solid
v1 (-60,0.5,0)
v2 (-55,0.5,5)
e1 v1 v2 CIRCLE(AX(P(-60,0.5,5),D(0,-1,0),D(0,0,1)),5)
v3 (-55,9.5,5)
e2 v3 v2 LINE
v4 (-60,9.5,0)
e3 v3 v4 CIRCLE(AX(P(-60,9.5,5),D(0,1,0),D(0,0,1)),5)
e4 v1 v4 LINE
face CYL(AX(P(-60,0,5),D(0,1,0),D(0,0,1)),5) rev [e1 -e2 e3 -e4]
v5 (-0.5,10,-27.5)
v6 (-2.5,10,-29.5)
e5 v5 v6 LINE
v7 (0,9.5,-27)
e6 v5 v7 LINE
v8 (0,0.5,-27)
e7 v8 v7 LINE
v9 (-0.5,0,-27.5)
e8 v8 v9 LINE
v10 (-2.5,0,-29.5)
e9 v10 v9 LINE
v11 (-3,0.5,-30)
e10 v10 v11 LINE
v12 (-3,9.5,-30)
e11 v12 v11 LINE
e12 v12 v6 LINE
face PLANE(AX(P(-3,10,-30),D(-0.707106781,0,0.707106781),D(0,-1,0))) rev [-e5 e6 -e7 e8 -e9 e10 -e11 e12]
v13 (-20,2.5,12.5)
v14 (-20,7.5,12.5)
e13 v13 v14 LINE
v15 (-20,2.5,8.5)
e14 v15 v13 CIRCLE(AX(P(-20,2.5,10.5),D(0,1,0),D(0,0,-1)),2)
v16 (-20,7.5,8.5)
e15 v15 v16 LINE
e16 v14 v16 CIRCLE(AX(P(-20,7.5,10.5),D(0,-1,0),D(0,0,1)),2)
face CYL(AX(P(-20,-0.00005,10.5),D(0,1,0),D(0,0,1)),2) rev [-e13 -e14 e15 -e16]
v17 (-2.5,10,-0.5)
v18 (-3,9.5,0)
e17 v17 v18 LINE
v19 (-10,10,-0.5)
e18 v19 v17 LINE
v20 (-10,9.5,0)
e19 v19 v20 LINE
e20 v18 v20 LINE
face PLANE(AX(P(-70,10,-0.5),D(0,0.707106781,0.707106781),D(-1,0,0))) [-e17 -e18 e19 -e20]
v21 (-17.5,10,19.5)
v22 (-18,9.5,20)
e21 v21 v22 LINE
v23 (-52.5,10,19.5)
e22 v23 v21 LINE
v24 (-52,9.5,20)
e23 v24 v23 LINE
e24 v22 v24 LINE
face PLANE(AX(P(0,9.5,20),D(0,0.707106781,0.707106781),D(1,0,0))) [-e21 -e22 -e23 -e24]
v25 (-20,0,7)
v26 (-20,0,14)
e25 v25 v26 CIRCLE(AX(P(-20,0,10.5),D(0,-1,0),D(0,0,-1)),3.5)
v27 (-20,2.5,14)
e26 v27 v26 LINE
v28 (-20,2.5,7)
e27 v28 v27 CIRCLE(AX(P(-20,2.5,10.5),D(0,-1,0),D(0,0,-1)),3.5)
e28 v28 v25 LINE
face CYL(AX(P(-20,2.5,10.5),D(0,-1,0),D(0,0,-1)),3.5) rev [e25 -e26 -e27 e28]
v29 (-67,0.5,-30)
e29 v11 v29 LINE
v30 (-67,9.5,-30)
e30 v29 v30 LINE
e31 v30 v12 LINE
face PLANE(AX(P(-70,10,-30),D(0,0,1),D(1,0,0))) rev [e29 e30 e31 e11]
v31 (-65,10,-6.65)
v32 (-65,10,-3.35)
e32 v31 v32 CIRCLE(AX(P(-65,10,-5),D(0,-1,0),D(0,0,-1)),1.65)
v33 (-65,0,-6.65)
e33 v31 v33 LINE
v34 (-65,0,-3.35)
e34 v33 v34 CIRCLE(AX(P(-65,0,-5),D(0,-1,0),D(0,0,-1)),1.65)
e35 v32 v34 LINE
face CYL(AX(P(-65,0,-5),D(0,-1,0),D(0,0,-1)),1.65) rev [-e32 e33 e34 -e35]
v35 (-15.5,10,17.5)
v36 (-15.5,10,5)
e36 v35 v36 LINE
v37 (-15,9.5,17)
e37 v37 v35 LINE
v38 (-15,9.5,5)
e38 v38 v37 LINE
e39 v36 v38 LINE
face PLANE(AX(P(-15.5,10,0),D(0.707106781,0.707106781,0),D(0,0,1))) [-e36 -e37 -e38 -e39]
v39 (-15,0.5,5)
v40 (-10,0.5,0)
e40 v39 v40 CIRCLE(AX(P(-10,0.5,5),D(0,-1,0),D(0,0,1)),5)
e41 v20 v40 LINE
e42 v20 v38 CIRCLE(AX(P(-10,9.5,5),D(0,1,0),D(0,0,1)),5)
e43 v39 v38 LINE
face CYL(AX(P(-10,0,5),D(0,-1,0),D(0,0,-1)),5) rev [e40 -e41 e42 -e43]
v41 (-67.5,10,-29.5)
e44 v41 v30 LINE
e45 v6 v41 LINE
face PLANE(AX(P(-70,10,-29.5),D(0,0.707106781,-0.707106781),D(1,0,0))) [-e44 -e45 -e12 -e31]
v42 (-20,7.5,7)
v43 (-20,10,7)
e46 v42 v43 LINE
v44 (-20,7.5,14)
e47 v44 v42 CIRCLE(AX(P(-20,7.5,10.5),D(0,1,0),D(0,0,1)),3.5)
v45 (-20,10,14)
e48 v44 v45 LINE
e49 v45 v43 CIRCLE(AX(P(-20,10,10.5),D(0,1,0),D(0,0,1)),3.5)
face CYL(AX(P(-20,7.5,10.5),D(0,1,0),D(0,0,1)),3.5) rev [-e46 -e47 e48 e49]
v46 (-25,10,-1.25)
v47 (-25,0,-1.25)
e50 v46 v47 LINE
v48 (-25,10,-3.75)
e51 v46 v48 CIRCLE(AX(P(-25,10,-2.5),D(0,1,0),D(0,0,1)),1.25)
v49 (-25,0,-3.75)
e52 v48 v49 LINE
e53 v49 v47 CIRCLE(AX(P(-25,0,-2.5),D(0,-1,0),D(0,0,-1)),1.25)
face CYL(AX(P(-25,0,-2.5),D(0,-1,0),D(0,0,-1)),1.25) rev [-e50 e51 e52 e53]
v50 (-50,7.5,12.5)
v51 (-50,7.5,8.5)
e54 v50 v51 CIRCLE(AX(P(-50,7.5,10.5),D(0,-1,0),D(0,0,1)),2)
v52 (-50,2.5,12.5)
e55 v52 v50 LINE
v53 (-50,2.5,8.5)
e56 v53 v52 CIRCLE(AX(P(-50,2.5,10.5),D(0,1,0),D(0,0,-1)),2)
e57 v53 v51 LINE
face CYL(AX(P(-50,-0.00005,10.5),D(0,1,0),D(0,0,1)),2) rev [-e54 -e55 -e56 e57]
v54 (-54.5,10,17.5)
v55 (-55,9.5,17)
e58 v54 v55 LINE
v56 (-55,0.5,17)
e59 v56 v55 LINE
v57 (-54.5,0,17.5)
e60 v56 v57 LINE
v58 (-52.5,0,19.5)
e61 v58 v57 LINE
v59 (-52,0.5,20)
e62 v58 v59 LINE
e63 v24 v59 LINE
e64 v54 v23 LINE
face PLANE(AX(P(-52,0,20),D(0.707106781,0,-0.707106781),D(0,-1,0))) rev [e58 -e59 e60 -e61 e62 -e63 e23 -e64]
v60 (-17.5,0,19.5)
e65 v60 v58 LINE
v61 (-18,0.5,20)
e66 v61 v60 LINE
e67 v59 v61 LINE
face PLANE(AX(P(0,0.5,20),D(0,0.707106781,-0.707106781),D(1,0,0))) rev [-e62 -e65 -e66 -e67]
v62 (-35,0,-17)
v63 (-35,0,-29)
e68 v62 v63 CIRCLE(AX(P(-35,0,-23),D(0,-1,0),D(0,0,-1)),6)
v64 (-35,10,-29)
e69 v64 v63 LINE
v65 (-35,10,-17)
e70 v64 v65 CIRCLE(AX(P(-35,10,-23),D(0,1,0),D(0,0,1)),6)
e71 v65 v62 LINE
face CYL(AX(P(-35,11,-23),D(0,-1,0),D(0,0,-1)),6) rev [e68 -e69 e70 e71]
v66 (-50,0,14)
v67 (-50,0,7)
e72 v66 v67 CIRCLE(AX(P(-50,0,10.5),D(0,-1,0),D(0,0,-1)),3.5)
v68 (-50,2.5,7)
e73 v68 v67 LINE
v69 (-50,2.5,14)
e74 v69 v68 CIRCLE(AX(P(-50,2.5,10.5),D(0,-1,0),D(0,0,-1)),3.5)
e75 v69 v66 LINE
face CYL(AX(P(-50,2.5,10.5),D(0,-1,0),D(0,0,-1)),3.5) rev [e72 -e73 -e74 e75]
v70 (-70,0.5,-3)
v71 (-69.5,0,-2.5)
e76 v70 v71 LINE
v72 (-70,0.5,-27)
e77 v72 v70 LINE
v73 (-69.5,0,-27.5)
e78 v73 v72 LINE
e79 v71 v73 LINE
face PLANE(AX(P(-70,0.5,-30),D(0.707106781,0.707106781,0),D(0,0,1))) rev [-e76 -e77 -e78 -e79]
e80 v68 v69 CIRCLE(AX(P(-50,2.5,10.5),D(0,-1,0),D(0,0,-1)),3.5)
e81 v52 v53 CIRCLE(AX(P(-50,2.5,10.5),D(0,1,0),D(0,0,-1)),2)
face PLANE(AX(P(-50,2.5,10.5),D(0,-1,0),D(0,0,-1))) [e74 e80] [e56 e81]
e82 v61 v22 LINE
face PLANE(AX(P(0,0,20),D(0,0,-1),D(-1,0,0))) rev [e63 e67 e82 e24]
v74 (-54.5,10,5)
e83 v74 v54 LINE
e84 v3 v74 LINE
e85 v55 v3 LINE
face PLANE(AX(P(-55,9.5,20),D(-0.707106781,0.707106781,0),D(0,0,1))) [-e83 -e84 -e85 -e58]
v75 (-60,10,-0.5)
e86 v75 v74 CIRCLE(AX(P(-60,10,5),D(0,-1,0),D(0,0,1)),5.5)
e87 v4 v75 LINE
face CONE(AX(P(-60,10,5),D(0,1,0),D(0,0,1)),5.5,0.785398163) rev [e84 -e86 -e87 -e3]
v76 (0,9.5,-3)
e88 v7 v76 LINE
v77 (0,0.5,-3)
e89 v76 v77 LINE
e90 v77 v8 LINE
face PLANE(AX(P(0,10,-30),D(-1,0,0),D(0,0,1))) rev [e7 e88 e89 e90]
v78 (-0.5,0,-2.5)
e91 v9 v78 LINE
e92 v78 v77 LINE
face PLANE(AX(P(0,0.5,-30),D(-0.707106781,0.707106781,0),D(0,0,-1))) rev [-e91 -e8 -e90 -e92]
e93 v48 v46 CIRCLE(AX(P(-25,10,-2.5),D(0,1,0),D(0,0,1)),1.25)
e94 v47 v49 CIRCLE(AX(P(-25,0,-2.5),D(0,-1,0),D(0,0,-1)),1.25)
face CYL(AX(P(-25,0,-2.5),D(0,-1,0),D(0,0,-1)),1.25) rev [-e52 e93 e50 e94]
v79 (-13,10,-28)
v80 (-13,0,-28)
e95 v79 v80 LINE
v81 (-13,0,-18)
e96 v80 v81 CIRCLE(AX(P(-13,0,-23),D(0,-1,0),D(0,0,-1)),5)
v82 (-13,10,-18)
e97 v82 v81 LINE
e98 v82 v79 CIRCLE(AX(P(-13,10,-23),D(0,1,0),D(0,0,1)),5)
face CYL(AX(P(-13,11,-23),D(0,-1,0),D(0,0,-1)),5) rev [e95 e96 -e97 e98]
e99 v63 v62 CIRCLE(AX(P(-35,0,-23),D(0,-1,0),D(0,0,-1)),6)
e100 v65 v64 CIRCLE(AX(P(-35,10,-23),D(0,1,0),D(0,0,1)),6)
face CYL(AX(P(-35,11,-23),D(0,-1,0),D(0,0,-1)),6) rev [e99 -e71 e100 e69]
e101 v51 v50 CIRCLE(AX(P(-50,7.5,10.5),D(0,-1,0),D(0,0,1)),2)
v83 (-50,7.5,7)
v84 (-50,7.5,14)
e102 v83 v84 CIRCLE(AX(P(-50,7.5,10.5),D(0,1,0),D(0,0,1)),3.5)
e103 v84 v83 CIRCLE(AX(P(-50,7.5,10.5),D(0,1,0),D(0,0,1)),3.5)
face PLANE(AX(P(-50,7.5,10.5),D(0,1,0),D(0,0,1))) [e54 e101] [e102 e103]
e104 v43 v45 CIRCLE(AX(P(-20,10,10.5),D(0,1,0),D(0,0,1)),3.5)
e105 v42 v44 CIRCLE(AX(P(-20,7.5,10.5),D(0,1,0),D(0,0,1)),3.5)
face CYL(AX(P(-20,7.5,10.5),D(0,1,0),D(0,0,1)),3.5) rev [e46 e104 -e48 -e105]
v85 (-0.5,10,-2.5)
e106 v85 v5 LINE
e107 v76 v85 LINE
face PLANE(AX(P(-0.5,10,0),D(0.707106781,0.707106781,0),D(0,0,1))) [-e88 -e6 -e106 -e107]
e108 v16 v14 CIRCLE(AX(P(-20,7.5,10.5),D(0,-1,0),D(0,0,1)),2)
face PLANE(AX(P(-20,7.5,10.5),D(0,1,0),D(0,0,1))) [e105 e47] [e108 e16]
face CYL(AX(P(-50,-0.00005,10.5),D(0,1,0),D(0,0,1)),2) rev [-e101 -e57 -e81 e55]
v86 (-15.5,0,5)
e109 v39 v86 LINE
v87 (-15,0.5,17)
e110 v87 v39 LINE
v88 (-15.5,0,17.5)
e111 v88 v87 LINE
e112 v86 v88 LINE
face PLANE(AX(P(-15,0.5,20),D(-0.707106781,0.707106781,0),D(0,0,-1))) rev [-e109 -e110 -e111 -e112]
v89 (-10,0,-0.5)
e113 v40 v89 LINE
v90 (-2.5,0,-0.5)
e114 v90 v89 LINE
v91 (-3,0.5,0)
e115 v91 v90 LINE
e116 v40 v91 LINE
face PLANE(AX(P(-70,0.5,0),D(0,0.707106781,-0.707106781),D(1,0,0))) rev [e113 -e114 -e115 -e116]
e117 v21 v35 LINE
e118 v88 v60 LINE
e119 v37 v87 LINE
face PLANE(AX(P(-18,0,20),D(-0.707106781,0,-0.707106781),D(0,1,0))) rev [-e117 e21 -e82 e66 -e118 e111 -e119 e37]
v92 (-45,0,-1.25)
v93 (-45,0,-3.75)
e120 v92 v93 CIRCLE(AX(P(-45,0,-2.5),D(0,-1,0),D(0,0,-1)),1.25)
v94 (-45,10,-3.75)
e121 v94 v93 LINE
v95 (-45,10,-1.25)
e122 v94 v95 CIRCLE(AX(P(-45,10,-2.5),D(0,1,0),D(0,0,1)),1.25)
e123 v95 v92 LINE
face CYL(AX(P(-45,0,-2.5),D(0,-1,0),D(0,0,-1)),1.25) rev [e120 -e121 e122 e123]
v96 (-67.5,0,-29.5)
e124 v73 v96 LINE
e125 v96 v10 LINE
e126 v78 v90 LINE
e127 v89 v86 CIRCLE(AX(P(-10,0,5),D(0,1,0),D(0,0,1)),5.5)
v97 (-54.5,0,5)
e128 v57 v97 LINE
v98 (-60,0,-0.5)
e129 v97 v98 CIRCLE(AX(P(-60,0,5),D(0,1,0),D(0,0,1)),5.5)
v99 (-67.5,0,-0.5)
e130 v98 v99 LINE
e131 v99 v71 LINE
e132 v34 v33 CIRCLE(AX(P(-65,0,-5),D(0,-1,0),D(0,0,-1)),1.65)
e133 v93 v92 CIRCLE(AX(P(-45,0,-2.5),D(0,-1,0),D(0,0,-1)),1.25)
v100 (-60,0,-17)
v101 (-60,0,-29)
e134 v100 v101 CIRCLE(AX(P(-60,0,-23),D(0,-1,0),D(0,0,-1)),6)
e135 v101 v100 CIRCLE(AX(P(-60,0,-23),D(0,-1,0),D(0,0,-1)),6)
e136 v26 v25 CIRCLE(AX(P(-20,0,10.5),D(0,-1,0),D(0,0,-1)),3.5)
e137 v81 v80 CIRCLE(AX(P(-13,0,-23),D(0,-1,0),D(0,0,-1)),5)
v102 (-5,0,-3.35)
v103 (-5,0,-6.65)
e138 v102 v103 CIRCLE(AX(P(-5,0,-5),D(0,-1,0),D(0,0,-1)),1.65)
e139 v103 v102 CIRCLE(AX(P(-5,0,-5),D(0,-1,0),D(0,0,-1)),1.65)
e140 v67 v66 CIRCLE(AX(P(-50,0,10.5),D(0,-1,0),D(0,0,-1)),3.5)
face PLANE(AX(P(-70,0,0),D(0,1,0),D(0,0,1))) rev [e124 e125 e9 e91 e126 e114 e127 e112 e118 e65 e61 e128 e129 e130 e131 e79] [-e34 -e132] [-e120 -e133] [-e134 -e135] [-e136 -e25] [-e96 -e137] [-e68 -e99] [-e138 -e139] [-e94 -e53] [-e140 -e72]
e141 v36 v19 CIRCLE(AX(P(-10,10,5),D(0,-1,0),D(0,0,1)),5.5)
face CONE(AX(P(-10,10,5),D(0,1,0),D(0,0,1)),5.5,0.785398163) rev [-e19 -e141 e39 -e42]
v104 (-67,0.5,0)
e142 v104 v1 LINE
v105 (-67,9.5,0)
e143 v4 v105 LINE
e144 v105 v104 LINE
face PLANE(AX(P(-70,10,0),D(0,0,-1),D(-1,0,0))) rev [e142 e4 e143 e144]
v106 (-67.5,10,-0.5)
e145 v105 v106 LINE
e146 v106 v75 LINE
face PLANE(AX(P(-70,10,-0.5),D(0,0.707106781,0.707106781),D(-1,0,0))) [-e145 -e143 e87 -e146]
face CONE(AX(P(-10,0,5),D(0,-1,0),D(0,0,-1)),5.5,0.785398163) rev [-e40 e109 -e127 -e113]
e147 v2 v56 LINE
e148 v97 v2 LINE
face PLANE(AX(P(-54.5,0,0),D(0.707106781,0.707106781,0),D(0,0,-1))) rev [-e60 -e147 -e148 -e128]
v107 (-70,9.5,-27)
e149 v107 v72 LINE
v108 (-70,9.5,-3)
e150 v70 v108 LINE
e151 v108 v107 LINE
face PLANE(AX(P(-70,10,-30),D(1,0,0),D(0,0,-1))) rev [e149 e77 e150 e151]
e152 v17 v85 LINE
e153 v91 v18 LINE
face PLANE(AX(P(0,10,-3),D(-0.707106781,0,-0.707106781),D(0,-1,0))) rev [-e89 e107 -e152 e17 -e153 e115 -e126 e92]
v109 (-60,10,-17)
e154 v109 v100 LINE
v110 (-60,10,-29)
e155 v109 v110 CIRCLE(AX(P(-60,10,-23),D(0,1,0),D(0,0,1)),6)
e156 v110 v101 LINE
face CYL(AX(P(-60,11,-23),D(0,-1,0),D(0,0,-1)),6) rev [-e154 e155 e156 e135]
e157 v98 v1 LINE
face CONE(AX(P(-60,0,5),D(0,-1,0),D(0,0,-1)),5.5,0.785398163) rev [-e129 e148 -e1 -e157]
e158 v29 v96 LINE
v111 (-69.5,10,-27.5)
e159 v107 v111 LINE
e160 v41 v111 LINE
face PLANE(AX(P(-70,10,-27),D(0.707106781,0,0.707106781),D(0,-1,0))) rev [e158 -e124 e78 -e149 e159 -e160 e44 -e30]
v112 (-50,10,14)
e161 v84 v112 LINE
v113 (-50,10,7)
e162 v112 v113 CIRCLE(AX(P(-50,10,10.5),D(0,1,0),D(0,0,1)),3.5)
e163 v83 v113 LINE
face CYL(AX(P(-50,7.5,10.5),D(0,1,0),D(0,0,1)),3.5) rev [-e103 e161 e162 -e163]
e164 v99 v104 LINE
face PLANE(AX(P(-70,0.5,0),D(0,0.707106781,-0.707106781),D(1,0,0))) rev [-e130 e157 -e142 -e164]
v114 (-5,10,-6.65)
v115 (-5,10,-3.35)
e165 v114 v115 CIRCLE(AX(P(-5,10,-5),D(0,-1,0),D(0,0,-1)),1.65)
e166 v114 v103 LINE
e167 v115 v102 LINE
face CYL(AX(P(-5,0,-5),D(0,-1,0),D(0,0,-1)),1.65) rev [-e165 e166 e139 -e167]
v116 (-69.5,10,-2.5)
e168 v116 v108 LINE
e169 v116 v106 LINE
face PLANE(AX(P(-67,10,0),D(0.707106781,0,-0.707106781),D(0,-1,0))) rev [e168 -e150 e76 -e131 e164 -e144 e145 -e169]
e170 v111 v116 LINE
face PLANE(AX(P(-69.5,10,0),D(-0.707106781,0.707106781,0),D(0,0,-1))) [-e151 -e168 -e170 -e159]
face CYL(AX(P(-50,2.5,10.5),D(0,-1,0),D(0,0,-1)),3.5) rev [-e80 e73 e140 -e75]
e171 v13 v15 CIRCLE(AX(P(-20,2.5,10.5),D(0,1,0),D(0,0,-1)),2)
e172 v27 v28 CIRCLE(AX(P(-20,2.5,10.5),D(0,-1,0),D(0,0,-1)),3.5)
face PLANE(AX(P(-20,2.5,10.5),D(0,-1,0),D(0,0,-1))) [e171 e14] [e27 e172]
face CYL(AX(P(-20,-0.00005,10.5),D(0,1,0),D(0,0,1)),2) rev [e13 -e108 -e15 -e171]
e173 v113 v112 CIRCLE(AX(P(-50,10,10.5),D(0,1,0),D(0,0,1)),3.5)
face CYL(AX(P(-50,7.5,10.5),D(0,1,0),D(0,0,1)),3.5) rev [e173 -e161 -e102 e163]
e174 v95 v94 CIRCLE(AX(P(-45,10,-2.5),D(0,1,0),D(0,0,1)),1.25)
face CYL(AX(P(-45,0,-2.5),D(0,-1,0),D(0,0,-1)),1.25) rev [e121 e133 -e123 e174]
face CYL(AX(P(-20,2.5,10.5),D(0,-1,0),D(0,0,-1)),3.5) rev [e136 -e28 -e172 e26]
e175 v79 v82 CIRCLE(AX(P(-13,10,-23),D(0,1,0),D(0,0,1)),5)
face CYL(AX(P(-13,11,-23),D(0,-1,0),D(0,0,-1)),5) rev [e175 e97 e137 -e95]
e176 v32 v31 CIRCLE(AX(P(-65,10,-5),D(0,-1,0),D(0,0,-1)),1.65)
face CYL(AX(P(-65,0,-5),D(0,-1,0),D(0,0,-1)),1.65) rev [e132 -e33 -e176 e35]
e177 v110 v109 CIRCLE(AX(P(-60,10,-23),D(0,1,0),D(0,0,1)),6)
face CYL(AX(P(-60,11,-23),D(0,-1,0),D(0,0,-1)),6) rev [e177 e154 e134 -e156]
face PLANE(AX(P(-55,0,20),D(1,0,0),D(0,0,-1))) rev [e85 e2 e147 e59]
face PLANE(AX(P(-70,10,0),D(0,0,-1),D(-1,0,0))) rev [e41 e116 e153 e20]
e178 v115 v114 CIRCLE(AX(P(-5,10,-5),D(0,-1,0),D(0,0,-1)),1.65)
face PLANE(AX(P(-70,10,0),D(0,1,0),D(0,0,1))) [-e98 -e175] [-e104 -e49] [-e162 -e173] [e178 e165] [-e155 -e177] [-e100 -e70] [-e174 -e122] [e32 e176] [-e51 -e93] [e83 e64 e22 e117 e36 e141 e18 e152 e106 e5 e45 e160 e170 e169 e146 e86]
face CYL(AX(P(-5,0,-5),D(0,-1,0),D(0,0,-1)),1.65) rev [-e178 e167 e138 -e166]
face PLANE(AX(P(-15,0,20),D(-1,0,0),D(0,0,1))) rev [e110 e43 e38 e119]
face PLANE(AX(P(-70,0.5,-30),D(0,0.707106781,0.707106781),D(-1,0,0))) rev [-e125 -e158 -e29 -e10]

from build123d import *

# Parameters (mm, degrees)
SKETCH1_W           = 70
SKETCH1_H           = 30
BOSS_EXTRUDE1_DEPTH = 10
SKETCH8_R           = 5
CUT_EXTRUDE6_DEPTH  = 11
SKETCH9_R           = 6
CUT_EXTRUDE7_DEPTH  = 11
M4_TAPPED_HOLE2_D   = 3.3
SKETCH13_W          = 40
SKETCH13_H          = 10
BOSS_EXTRUDE2_DEPTH = 20
SKETCH14_R          = 2
CUT_EXTRUDE8_DEPTH  = 77.811457479
M3_TAPPED_HOLE1_D   = 2.5
CHAMFER3_SIZE       = 3
FILLET1_R           = 5
CHAMFER4_SIZE       = 0.5
SKETCH18_R          = 3.5
CUT_EXTRUDE9_DEPTH  = 2.5
CUT_EXTRUDE10_START = -2.5
SKETCH19_R          = 3.5
CUT_EXTRUDE10_DEPTH = 2.5


with BuildPart() as part:
    # Sketch1 → Boss-Extrude1 (new body)
    with BuildSketch(Plane(origin=(0, 0, 0), x_dir=(1, 0, 0), z_dir=(0, 1, 0))):
        with Locations((-35, 15)):
            Rectangle(SKETCH1_W, SKETCH1_H)
    extrude(amount=BOSS_EXTRUDE1_DEPTH)

    # Sketch8 → Cut-Extrude6 (cut)
    with BuildSketch(Plane.XZ):
        with Locations(Location((-13, -23, 0), (0, 0, 270))):
            Circle(SKETCH8_R)
    extrude(amount=-CUT_EXTRUDE6_DEPTH, mode=Mode.SUBTRACT)

    # Sketch9 → Cut-Extrude7 (cut)
    with BuildSketch(Plane.XZ):
        with Locations(Location((-60, -23, 0), (0, 0, 270))):
            Circle(SKETCH9_R)
        with Locations(Location((-35, -23, 0), (0, 0, 270))):
            Circle(SKETCH9_R)
    extrude(amount=-CUT_EXTRUDE7_DEPTH, mode=Mode.SUBTRACT)

    # M4 Tapped Hole2 (through all)
    with Locations(Plane(origin=(0, 0, 0), x_dir=(-1, 0, 0), z_dir=(0, -1, 0))):
        with Locations((65, 5), (5, 5)):
            Hole(M4_TAPPED_HOLE2_D / 2)

    # Sketch13 → Boss-Extrude2 (add)
    with BuildSketch(Plane.XY):
        with Locations((-35, 5)):
            Rectangle(SKETCH13_W, SKETCH13_H)
    extrude(amount=BOSS_EXTRUDE2_DEPTH)

    # Sketch14 → Cut-Extrude8 (cut, through all)
    with BuildSketch(Plane(origin=(0, 10, 0), x_dir=(1, 0, 0), z_dir=(0, 1, 0))):
        with Locations(Location((-50, -10.5, 0), (0, 0, 270))):
            Circle(SKETCH14_R)
        with Locations(Location((-20, -10.5, 0), (0, 0, 270))):
            Circle(SKETCH14_R)
    extrude(amount=-CUT_EXTRUDE8_DEPTH, mode=Mode.SUBTRACT)

    # M3 Tapped Hole1 (through all)
    with Locations(Plane(origin=(0, 0, 0), x_dir=(-1, 0, 0), z_dir=(0, -1, 0))):
        with Locations((25, 2.5), (45, 2.5)):
            Hole(M3_TAPPED_HOLE1_D / 2)

    # Chamfer3
    chamfer3_edges = [part.edges().sort_by_distance(p)[0] for p in [
        (0, 5, -30),
        (0, 5, 0),
        (-15, 5, 20),
        (-55, 5, 20),
        (-70, 5, 0),
        (-70, 5, -30),
    ]]
    chamfer(chamfer3_edges, length=CHAMFER3_SIZE)

    # Fillet1
    fillet1_edges = [part.edges().sort_by_distance(p)[0] for p in [
        (-15, 5, 0),
        (-55, 5, 0),
    ]]
    fillet(fillet1_edges, radius=FILLET1_R)

    # Chamfer4
    chamfer4_edges = [part.edges().sort_by_distance(p)[0] for p in [
        (-6.5, 0, 0),
        (-6.5, 10, 0),
        (-13.535533906, 10, 1.464466094),
        (-13.535533906, 0, 1.464466094),
        (-56.464466094, 0, 1.464466094),
        (-56.464466094, 10, 1.464466094),
        (-35, 0, -30),
        (-35, 10, -30),
        (-70, 0, -15),
        (0, 0, -15),
        (-15, 0, 11),
        (-35, 0, 20),
        (-55, 0, 11),
        (-63.5, 0, 0),
        (0, 10, -15),
        (-70, 10, -15),
        (-63.5, 10, 0),
        (-55, 10, 11),
        (-35, 10, 20),
        (-15, 10, 11),
    ]]
    chamfer(chamfer4_edges, length=CHAMFER4_SIZE)

    # Sketch18 → Cut-Extrude9 (cut)
    with BuildSketch(Plane(origin=(0, 10, 0), x_dir=(1, 0, 0), z_dir=(0, 1, 0))):
        with Locations(Location((-50, -10.5, 0), (0, 0, 270))):
            Circle(SKETCH18_R)
        with Locations(Location((-20, -10.5, 0), (0, 0, 270))):
            Circle(SKETCH18_R)
    extrude(amount=-CUT_EXTRUDE9_DEPTH, mode=Mode.SUBTRACT)

    # Sketch19 → Cut-Extrude10 (cut)
    with BuildSketch(Plane.XZ.offset(CUT_EXTRUDE10_START)):
        with Locations(Location((-50, 10.5, 0), (0, 0, 90))):
            Circle(SKETCH19_R)
        with Locations(Location((-20, 10.5, 0), (0, 0, 90))):
            Circle(SKETCH19_R)
    extrude(amount=CUT_EXTRUDE10_DEPTH, mode=Mode.SUBTRACT)


solid = part.part
